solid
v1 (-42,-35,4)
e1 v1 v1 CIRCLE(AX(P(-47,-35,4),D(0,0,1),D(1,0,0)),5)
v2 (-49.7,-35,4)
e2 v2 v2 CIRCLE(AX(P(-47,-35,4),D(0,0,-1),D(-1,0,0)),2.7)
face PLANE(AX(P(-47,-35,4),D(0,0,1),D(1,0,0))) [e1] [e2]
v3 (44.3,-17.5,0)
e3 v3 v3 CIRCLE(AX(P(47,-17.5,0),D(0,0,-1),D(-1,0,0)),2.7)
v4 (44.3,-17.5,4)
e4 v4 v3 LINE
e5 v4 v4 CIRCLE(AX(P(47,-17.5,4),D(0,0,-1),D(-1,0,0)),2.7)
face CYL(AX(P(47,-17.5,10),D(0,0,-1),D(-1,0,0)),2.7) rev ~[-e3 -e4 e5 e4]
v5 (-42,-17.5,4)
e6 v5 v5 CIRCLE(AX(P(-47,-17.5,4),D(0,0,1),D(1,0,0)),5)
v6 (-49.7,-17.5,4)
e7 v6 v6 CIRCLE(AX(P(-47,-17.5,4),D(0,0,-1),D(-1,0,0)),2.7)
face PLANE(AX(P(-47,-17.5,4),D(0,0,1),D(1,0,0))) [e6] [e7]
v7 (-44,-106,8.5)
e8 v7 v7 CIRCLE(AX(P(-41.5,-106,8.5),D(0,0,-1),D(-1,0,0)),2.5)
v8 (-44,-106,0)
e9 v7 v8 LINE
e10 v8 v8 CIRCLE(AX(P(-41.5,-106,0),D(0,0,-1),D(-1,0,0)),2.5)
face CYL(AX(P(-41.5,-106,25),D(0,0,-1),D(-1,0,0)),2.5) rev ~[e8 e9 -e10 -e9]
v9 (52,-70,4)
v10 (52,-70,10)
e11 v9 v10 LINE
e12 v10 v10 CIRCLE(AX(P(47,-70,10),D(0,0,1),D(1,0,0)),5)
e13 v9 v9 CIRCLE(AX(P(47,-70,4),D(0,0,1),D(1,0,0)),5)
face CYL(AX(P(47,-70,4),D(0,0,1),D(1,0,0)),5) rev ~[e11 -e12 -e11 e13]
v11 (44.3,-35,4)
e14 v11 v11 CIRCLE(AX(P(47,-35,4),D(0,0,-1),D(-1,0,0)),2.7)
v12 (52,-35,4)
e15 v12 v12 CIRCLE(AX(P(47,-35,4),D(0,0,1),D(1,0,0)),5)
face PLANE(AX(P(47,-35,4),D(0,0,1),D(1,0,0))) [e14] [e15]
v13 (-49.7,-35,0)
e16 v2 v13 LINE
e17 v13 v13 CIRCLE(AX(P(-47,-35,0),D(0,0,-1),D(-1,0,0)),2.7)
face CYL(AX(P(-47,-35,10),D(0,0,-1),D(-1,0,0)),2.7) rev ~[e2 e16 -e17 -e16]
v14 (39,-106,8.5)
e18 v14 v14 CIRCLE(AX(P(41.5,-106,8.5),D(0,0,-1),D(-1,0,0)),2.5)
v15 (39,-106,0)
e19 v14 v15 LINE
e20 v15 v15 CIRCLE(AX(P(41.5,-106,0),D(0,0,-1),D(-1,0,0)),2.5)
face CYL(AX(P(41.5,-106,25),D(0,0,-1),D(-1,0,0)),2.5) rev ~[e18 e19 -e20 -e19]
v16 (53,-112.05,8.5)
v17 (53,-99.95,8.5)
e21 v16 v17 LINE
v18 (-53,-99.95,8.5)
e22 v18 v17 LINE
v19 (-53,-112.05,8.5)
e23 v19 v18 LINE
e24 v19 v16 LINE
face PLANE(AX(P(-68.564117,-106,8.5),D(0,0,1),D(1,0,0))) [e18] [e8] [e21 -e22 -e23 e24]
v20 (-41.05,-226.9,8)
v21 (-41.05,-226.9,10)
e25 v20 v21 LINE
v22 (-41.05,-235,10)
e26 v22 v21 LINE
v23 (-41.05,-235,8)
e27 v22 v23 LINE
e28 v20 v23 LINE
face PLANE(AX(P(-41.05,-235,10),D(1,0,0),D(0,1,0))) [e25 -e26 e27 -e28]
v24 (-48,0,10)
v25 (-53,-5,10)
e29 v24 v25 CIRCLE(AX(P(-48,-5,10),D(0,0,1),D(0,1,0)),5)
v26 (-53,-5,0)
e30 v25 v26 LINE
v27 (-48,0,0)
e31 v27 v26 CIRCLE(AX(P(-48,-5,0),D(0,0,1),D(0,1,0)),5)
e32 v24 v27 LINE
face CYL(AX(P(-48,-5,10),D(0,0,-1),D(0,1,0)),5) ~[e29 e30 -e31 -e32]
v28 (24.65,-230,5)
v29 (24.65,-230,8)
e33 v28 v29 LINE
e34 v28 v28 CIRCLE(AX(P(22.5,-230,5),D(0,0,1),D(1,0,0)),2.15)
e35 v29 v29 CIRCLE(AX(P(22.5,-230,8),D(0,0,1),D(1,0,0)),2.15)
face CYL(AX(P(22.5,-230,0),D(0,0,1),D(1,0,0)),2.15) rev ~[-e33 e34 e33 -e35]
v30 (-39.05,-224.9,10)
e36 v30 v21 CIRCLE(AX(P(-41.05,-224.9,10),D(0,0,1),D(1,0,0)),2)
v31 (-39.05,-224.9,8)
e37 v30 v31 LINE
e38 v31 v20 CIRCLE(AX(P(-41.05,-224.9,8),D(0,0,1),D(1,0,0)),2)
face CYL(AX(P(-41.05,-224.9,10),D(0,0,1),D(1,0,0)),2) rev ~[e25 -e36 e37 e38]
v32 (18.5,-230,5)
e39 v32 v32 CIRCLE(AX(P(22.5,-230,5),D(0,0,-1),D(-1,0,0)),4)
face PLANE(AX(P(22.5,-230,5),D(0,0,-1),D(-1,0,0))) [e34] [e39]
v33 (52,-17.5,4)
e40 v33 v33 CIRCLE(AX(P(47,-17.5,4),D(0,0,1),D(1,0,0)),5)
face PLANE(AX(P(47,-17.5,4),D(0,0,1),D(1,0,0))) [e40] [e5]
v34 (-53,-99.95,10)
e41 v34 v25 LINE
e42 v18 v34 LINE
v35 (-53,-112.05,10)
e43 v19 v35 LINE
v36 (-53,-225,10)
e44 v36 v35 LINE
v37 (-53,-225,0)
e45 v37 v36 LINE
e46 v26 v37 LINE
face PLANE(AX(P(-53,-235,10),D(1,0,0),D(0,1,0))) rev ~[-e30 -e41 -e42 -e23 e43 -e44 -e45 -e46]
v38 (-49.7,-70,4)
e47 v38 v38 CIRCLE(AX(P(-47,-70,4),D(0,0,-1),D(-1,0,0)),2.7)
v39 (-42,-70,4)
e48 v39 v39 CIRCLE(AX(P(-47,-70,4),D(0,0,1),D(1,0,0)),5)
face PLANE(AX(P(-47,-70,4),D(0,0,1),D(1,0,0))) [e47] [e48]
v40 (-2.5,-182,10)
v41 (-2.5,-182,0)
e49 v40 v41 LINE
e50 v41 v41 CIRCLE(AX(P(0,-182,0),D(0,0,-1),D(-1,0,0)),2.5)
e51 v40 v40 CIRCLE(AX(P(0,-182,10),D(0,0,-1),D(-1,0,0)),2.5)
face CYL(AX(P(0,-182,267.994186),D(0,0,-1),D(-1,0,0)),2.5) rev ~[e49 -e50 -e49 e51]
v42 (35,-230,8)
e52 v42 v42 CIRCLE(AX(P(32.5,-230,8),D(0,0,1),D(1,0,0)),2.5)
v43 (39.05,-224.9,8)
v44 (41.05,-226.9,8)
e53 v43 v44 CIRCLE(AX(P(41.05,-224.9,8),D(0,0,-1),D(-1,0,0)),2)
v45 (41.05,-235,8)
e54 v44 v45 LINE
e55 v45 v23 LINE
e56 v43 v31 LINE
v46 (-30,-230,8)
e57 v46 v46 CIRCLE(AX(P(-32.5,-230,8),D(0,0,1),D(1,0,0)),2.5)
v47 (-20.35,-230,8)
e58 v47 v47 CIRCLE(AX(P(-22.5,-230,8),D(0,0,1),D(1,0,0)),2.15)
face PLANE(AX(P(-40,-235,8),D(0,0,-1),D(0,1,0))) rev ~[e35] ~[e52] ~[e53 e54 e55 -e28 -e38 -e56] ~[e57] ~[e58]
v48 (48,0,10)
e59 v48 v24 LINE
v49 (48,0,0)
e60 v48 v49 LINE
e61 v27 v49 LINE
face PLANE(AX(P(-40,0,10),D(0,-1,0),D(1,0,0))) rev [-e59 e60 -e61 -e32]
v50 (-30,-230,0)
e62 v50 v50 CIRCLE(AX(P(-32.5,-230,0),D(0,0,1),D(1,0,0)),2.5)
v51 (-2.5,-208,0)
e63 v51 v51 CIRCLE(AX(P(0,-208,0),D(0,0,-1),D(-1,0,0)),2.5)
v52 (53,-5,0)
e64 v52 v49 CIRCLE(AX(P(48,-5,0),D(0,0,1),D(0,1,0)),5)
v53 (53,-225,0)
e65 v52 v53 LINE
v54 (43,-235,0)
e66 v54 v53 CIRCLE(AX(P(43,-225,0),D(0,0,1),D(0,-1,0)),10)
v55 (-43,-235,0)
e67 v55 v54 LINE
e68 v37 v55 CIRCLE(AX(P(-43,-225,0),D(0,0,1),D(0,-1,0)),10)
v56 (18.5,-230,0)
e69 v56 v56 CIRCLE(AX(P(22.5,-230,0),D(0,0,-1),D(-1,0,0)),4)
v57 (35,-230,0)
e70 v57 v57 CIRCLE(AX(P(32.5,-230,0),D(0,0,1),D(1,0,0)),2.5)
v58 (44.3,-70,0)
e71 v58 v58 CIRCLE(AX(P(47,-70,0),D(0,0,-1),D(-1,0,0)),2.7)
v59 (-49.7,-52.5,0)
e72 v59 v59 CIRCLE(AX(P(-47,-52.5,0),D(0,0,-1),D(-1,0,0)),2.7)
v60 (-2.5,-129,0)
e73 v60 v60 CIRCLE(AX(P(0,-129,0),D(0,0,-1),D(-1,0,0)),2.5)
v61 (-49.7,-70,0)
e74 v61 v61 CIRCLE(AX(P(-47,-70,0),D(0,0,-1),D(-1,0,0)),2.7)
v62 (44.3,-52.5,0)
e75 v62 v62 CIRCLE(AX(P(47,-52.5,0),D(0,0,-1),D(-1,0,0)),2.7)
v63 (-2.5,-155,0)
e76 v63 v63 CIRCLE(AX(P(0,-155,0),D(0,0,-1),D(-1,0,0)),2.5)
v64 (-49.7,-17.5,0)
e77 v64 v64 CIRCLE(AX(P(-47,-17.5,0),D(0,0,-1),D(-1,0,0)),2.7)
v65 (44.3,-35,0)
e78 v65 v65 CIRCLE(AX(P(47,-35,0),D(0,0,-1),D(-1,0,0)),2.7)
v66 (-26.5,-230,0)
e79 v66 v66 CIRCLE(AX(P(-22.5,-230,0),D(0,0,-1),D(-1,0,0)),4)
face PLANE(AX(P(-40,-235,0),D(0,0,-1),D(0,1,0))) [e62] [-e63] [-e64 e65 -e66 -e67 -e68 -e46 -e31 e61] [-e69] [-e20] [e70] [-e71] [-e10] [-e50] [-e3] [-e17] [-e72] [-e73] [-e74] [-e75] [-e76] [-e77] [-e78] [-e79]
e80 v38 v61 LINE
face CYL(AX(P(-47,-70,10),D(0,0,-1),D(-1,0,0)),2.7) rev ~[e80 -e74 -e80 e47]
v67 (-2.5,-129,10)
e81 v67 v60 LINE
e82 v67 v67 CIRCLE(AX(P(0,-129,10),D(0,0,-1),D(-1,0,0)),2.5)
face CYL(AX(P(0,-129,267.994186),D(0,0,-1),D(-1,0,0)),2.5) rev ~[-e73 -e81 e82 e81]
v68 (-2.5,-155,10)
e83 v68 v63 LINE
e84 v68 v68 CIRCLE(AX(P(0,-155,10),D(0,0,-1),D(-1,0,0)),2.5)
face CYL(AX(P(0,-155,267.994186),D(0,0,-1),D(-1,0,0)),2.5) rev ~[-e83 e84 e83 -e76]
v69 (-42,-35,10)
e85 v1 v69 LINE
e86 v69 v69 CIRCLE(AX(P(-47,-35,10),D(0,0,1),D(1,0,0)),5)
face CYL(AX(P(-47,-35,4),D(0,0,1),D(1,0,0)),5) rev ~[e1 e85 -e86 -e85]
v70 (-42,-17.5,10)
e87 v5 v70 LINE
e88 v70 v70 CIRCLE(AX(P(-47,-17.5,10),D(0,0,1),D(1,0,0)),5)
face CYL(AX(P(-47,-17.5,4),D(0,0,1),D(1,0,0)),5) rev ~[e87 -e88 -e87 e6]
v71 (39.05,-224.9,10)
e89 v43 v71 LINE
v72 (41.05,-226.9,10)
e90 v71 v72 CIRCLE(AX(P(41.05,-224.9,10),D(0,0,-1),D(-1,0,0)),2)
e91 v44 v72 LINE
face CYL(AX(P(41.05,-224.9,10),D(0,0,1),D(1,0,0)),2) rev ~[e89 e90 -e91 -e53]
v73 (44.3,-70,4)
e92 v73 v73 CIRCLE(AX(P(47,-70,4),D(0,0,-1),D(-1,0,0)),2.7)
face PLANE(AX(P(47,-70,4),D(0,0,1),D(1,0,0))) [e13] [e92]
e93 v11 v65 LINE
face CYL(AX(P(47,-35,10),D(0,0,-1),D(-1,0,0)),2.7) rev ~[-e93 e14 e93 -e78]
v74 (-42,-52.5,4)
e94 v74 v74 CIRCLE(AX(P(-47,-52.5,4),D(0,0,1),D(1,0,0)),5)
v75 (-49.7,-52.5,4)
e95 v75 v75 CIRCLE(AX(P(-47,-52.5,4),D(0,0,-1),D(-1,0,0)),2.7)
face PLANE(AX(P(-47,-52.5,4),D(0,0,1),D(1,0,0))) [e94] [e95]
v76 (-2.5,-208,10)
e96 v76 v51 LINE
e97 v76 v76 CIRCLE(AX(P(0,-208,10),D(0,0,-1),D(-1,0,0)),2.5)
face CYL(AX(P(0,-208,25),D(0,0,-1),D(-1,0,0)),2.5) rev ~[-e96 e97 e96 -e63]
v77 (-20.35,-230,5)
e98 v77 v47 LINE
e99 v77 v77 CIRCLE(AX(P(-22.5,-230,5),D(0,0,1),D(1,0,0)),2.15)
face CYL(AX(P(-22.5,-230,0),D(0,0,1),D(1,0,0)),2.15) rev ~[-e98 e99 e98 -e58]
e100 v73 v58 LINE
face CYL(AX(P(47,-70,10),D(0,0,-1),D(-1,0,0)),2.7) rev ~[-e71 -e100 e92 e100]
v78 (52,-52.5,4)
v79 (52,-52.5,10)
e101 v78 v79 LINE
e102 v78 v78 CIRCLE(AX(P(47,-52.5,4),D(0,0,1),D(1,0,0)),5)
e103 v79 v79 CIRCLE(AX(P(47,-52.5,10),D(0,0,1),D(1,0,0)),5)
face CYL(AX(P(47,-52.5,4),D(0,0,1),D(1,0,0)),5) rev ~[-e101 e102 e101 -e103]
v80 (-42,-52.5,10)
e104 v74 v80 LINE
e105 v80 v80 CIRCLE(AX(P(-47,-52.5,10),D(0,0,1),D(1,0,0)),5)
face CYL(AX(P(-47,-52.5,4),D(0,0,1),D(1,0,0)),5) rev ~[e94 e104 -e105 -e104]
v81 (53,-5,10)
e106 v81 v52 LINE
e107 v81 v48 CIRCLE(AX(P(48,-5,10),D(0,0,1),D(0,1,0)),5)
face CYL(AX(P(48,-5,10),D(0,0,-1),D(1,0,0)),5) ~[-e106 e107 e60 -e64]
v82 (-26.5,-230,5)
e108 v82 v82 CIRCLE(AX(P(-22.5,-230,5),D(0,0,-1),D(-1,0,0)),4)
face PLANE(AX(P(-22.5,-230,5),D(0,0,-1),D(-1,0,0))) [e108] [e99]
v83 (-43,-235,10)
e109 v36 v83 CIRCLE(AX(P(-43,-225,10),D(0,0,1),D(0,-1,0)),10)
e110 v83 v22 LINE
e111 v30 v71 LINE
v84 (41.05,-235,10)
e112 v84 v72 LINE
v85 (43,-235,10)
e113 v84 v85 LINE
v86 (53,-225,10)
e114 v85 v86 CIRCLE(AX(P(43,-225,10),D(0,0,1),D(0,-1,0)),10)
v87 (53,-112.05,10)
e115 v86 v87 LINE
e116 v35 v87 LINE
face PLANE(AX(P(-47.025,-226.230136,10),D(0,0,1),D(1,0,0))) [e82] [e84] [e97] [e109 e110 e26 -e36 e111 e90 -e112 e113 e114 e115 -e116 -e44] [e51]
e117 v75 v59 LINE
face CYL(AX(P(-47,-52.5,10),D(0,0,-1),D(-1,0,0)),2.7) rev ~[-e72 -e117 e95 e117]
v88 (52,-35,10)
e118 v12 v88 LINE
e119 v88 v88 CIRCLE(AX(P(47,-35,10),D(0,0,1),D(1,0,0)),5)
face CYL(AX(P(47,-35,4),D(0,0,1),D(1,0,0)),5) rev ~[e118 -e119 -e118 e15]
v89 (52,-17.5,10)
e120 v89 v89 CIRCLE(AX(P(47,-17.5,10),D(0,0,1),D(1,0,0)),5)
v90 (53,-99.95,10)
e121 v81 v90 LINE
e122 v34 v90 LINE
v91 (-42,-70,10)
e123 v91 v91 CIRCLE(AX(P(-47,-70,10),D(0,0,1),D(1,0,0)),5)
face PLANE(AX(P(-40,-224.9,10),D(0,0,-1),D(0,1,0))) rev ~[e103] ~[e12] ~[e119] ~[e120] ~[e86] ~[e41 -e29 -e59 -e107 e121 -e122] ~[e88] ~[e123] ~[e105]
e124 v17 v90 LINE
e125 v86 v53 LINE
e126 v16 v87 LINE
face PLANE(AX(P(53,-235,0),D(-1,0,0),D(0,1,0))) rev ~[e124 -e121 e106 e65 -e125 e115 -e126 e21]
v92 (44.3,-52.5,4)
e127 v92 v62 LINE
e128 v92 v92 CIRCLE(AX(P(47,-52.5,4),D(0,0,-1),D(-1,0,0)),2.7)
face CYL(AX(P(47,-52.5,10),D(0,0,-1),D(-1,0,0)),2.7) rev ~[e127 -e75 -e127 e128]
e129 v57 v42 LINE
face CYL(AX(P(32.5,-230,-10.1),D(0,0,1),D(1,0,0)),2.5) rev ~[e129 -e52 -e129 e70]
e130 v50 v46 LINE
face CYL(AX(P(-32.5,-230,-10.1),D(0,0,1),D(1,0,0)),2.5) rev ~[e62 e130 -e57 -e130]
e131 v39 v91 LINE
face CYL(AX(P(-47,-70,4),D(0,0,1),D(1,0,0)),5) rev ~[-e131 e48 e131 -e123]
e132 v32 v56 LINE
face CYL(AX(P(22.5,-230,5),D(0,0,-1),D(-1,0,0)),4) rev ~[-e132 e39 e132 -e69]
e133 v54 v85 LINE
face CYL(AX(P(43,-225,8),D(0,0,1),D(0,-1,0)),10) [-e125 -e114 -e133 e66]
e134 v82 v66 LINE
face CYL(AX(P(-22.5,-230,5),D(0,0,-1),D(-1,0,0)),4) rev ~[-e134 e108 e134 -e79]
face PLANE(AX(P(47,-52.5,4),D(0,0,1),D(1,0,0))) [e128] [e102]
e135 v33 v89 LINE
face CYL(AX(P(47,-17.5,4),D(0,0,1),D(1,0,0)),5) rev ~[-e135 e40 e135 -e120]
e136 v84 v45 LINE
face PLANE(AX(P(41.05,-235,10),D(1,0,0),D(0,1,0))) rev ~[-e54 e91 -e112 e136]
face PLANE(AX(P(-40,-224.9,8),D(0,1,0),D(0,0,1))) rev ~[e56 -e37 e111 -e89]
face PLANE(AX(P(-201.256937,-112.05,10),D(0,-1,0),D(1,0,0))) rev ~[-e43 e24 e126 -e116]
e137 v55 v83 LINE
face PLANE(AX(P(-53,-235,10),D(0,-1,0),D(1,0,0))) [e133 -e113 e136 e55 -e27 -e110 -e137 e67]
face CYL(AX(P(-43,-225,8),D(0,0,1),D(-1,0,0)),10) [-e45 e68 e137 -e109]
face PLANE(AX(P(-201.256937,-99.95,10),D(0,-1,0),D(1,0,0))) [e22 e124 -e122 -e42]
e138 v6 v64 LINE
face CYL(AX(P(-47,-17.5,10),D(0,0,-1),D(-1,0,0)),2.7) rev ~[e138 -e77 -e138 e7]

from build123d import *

# Parameters (mm, degrees)
SKETCH_1_W                = 80
SKETCH_1_H                = 235
EXTRUDE_1_DEPTH           = 10
SKETCH_20_W               = 82
SKETCH_20_H               = 14.219263271
CUT_EXTRUDE_3_DEPTH       = 2
HOLE_WIZARD_4_D           = 4.3
HOLE_WIZARD_4_CBORE_D     = 8
HOLE_WIZARD_4_CBORE_DEPTH = 5
SKETCH_26_W               = 13
SKETCH_26_H               = 87.5
EXTRUDE_3_DEPTH           = 10
FILLET_5_R                = 5
HOLE_WIZARD_1_D           = 5.4
HOLE_WIZARD_1_CBORE_D     = 10
HOLE_WIZARD_1_CBORE_DEPTH = 6
PATTERN_LINEAR_2_COUNT    = 2
PATTERN_LINEAR_2_PITCH    = 17.5
MOVE_FACE_1_BY            = 13
MOVE_FACE_1_2_BY          = 13
SKETCH_30_W               = 265.385639797
SKETCH_30_H               = 12.1
CUT_EXTRUDE_7_DEPTH       = 1.5
SKETCH_31_W               = 11.95
SKETCH_31_H               = 17.539728067
SKETCH_31_H_2             = 20.784895231
EXTRUDE_4_DEPTH           = 10
SKETCH_32_R               = 2
CUT_EXTRUDE_8_DEPTH       = 2
MM_1_D                    = 5
MM_1_DEPTH                = 10.1
MM_1_TIP                  = 1.502151548
FILLET_6_R                = 10
HOLE_WIZARD_M6_1_D        = 5
HOLE_WIZARD_M6_1_DEPTH    = 15
HOLE_WIZARD_M6_1_TIP      = 1.502151548
HOLE_WIZARD_M6_2_D        = 5
HOLE_WIZARD_M6_2_DEPTH    = 15
HOLE_WIZARD_M6_2_TIP      = 1.502151548
HOLE_WIZARD_M6_3_D        = 5
HOLE_WIZARD_M6_4_D        = 5


with BuildPart() as part:
    # 草图1 → 凸台-拉伸1 (new body)
    with BuildSketch(Plane.XY):
        with Locations((0, -117.5)):
            Rectangle(SKETCH_1_W, SKETCH_1_H)
    extrude(amount=EXTRUDE_1_DEPTH)

    # 草图20 → 切除-拉伸3 (cut)
    with BuildSketch(Plane.XY.offset(10)):
        with Locations((0, -232.009631635)):
            Rectangle(SKETCH_20_W, SKETCH_20_H)
    extrude(amount=-CUT_EXTRUDE_3_DEPTH, mode=Mode.SUBTRACT)

    # 打孔尺寸(%根据)开槽圆柱头螺钉的类型4 (through all)
    with Locations(Plane(origin=(0, 0, 0), x_dir=(-1, 0, 0), z_dir=(0, 0, -1))):
        with Locations((-22.5, -230), (22.5, -230)):
            CounterBoreHole(HOLE_WIZARD_4_D / 2, HOLE_WIZARD_4_CBORE_D / 2, HOLE_WIZARD_4_CBORE_DEPTH)

    # 草图26 → 凸台-拉伸3 (add)
    with BuildSketch(Plane.XY.offset(10)):
        with Locations((46.5, -43.75)):
            Rectangle(SKETCH_26_W, SKETCH_26_H)
    extrude_3 = extrude(amount=-EXTRUDE_3_DEPTH)

    # 镜向1: 凸台-拉伸3 across plane
    add(extrude_3.mirror(Plane(origin=(0, 0, 0), x_dir=(0, 0, 1), z_dir=(1, 0, 0))))

    # 圆角5
    fillet_5_edges = [part.edges().sort_by_distance(p)[0] for p in [
        (53, 0, 5),
        (-53, 0, 5),
    ]]
    fillet(fillet_5_edges, radius=FILLET_5_R)

    # 打孔尺寸(%根据)内六角圆柱头螺钉的类型1 (through all)
    with Locations(Plane.XY.offset(10)):
        with Locations((-47, -17.5), (-47, -52.5), (47, -52.5), (47, -17.5)):
            hole_wizard_1 = CounterBoreHole(HOLE_WIZARD_1_D / 2, HOLE_WIZARD_1_CBORE_D / 2, HOLE_WIZARD_1_CBORE_DEPTH)

    # 阵列(线性)2: 打孔尺寸(%根据)内六角圆柱头螺钉的类型1 ×2
    with Locations(*[(0, -i * PATTERN_LINEAR_2_PITCH, 0) for i in range(1, PATTERN_LINEAR_2_COUNT)]):
        add(hole_wizard_1, mode=Mode.SUBTRACT)

    # Move Face 1: a face moved outward by 13.0
    extrude(part.faces().sort_by_distance((40, -160.296095683, 4.94445972))[0], amount=MOVE_FACE_1_BY, dir=(1, 0, 0))

    # Move Face 1 2: a face moved outward by 13.0
    extrude(part.faces().sort_by_distance((-40, -160.296095683, 4.94445972))[0], amount=MOVE_FACE_1_2_BY, dir=(-1, 0, 0))

    # 草图30 → 切除-拉伸7 (cut)
    with BuildSketch(Plane.XY.offset(10)):
        with Locations((-68.564117246, -106)):
            Rectangle(SKETCH_30_W, SKETCH_30_H)
    extrude(amount=-CUT_EXTRUDE_7_DEPTH, mode=Mode.SUBTRACT)

    # 草图31 → 凸台-拉伸4 (add)
    with BuildSketch(Plane.XY.offset(10)):
        with Locations((-47.025, -226.230135967)):
            Rectangle(SKETCH_31_W, SKETCH_31_H)
        with Locations((47.025, -224.607552385)):
            Rectangle(SKETCH_31_W, SKETCH_31_H_2)
    extrude(amount=-EXTRUDE_4_DEPTH)

    # 草图32 → 切除-拉伸8 (cut)
    with BuildSketch(Plane.XY.offset(10)):
        with Locations((-41.05, -224.9)):
            Circle(SKETCH_32_R)
        with Locations((41.05, -224.9)):
            Circle(SKETCH_32_R)
    extrude(amount=-CUT_EXTRUDE_8_DEPTH, mode=Mode.SUBTRACT)

    # 大小mm 暗销孔1
    with Locations(Plane(origin=(0, 0, 0), x_dir=(-1, 0, 0), z_dir=(0, 0, -1))):
        with Locations((-32.5, -230), (32.5, -230)):
            Hole(MM_1_D / 2, depth=MM_1_DEPTH)
            with Locations((0, 0, -(MM_1_DEPTH + MM_1_TIP / 2))):  # 118° drill point
                Cone(0, MM_1_D / 2, MM_1_TIP, mode=Mode.SUBTRACT)

    # 圆角6
    fillet_6_edges = [part.edges().sort_by_distance(p)[0] for p in [
        (53, -235, 5),
        (-53, -235, 5),
    ]]
    fillet(fillet_6_edges, radius=FILLET_6_R)

    # M6 螺纹孔1
    with Locations(Plane.XY.offset(10)):
        with Locations((-41.5, -106), (41.5, -106)):
            Hole(HOLE_WIZARD_M6_1_D / 2, depth=HOLE_WIZARD_M6_1_DEPTH)
            with Locations((0, 0, -(HOLE_WIZARD_M6_1_DEPTH + HOLE_WIZARD_M6_1_TIP / 2))):  # 118° drill point
                Cone(0, HOLE_WIZARD_M6_1_D / 2, HOLE_WIZARD_M6_1_TIP, mode=Mode.SUBTRACT)

    # M6 螺纹孔2
    with Locations(Plane.XY.offset(10)):
        with Locations((0, -208)):
            Hole(HOLE_WIZARD_M6_2_D / 2, depth=HOLE_WIZARD_M6_2_DEPTH)
            with Locations((0, 0, -(HOLE_WIZARD_M6_2_DEPTH + HOLE_WIZARD_M6_2_TIP / 2))):  # 118° drill point
                Cone(0, HOLE_WIZARD_M6_2_D / 2, HOLE_WIZARD_M6_2_TIP, mode=Mode.SUBTRACT)

    # M6 螺纹孔3 (through all)
    with Locations(Plane.XY.offset(10)):
        with Locations((0, -155), (0, -182)):
            Hole(HOLE_WIZARD_M6_3_D / 2)

    # M6 螺纹孔4 (through all)
    with Locations(Plane.XY.offset(10)):
        with Locations((0, -129)):
            Hole(HOLE_WIZARD_M6_4_D / 2)


solid = part.part
